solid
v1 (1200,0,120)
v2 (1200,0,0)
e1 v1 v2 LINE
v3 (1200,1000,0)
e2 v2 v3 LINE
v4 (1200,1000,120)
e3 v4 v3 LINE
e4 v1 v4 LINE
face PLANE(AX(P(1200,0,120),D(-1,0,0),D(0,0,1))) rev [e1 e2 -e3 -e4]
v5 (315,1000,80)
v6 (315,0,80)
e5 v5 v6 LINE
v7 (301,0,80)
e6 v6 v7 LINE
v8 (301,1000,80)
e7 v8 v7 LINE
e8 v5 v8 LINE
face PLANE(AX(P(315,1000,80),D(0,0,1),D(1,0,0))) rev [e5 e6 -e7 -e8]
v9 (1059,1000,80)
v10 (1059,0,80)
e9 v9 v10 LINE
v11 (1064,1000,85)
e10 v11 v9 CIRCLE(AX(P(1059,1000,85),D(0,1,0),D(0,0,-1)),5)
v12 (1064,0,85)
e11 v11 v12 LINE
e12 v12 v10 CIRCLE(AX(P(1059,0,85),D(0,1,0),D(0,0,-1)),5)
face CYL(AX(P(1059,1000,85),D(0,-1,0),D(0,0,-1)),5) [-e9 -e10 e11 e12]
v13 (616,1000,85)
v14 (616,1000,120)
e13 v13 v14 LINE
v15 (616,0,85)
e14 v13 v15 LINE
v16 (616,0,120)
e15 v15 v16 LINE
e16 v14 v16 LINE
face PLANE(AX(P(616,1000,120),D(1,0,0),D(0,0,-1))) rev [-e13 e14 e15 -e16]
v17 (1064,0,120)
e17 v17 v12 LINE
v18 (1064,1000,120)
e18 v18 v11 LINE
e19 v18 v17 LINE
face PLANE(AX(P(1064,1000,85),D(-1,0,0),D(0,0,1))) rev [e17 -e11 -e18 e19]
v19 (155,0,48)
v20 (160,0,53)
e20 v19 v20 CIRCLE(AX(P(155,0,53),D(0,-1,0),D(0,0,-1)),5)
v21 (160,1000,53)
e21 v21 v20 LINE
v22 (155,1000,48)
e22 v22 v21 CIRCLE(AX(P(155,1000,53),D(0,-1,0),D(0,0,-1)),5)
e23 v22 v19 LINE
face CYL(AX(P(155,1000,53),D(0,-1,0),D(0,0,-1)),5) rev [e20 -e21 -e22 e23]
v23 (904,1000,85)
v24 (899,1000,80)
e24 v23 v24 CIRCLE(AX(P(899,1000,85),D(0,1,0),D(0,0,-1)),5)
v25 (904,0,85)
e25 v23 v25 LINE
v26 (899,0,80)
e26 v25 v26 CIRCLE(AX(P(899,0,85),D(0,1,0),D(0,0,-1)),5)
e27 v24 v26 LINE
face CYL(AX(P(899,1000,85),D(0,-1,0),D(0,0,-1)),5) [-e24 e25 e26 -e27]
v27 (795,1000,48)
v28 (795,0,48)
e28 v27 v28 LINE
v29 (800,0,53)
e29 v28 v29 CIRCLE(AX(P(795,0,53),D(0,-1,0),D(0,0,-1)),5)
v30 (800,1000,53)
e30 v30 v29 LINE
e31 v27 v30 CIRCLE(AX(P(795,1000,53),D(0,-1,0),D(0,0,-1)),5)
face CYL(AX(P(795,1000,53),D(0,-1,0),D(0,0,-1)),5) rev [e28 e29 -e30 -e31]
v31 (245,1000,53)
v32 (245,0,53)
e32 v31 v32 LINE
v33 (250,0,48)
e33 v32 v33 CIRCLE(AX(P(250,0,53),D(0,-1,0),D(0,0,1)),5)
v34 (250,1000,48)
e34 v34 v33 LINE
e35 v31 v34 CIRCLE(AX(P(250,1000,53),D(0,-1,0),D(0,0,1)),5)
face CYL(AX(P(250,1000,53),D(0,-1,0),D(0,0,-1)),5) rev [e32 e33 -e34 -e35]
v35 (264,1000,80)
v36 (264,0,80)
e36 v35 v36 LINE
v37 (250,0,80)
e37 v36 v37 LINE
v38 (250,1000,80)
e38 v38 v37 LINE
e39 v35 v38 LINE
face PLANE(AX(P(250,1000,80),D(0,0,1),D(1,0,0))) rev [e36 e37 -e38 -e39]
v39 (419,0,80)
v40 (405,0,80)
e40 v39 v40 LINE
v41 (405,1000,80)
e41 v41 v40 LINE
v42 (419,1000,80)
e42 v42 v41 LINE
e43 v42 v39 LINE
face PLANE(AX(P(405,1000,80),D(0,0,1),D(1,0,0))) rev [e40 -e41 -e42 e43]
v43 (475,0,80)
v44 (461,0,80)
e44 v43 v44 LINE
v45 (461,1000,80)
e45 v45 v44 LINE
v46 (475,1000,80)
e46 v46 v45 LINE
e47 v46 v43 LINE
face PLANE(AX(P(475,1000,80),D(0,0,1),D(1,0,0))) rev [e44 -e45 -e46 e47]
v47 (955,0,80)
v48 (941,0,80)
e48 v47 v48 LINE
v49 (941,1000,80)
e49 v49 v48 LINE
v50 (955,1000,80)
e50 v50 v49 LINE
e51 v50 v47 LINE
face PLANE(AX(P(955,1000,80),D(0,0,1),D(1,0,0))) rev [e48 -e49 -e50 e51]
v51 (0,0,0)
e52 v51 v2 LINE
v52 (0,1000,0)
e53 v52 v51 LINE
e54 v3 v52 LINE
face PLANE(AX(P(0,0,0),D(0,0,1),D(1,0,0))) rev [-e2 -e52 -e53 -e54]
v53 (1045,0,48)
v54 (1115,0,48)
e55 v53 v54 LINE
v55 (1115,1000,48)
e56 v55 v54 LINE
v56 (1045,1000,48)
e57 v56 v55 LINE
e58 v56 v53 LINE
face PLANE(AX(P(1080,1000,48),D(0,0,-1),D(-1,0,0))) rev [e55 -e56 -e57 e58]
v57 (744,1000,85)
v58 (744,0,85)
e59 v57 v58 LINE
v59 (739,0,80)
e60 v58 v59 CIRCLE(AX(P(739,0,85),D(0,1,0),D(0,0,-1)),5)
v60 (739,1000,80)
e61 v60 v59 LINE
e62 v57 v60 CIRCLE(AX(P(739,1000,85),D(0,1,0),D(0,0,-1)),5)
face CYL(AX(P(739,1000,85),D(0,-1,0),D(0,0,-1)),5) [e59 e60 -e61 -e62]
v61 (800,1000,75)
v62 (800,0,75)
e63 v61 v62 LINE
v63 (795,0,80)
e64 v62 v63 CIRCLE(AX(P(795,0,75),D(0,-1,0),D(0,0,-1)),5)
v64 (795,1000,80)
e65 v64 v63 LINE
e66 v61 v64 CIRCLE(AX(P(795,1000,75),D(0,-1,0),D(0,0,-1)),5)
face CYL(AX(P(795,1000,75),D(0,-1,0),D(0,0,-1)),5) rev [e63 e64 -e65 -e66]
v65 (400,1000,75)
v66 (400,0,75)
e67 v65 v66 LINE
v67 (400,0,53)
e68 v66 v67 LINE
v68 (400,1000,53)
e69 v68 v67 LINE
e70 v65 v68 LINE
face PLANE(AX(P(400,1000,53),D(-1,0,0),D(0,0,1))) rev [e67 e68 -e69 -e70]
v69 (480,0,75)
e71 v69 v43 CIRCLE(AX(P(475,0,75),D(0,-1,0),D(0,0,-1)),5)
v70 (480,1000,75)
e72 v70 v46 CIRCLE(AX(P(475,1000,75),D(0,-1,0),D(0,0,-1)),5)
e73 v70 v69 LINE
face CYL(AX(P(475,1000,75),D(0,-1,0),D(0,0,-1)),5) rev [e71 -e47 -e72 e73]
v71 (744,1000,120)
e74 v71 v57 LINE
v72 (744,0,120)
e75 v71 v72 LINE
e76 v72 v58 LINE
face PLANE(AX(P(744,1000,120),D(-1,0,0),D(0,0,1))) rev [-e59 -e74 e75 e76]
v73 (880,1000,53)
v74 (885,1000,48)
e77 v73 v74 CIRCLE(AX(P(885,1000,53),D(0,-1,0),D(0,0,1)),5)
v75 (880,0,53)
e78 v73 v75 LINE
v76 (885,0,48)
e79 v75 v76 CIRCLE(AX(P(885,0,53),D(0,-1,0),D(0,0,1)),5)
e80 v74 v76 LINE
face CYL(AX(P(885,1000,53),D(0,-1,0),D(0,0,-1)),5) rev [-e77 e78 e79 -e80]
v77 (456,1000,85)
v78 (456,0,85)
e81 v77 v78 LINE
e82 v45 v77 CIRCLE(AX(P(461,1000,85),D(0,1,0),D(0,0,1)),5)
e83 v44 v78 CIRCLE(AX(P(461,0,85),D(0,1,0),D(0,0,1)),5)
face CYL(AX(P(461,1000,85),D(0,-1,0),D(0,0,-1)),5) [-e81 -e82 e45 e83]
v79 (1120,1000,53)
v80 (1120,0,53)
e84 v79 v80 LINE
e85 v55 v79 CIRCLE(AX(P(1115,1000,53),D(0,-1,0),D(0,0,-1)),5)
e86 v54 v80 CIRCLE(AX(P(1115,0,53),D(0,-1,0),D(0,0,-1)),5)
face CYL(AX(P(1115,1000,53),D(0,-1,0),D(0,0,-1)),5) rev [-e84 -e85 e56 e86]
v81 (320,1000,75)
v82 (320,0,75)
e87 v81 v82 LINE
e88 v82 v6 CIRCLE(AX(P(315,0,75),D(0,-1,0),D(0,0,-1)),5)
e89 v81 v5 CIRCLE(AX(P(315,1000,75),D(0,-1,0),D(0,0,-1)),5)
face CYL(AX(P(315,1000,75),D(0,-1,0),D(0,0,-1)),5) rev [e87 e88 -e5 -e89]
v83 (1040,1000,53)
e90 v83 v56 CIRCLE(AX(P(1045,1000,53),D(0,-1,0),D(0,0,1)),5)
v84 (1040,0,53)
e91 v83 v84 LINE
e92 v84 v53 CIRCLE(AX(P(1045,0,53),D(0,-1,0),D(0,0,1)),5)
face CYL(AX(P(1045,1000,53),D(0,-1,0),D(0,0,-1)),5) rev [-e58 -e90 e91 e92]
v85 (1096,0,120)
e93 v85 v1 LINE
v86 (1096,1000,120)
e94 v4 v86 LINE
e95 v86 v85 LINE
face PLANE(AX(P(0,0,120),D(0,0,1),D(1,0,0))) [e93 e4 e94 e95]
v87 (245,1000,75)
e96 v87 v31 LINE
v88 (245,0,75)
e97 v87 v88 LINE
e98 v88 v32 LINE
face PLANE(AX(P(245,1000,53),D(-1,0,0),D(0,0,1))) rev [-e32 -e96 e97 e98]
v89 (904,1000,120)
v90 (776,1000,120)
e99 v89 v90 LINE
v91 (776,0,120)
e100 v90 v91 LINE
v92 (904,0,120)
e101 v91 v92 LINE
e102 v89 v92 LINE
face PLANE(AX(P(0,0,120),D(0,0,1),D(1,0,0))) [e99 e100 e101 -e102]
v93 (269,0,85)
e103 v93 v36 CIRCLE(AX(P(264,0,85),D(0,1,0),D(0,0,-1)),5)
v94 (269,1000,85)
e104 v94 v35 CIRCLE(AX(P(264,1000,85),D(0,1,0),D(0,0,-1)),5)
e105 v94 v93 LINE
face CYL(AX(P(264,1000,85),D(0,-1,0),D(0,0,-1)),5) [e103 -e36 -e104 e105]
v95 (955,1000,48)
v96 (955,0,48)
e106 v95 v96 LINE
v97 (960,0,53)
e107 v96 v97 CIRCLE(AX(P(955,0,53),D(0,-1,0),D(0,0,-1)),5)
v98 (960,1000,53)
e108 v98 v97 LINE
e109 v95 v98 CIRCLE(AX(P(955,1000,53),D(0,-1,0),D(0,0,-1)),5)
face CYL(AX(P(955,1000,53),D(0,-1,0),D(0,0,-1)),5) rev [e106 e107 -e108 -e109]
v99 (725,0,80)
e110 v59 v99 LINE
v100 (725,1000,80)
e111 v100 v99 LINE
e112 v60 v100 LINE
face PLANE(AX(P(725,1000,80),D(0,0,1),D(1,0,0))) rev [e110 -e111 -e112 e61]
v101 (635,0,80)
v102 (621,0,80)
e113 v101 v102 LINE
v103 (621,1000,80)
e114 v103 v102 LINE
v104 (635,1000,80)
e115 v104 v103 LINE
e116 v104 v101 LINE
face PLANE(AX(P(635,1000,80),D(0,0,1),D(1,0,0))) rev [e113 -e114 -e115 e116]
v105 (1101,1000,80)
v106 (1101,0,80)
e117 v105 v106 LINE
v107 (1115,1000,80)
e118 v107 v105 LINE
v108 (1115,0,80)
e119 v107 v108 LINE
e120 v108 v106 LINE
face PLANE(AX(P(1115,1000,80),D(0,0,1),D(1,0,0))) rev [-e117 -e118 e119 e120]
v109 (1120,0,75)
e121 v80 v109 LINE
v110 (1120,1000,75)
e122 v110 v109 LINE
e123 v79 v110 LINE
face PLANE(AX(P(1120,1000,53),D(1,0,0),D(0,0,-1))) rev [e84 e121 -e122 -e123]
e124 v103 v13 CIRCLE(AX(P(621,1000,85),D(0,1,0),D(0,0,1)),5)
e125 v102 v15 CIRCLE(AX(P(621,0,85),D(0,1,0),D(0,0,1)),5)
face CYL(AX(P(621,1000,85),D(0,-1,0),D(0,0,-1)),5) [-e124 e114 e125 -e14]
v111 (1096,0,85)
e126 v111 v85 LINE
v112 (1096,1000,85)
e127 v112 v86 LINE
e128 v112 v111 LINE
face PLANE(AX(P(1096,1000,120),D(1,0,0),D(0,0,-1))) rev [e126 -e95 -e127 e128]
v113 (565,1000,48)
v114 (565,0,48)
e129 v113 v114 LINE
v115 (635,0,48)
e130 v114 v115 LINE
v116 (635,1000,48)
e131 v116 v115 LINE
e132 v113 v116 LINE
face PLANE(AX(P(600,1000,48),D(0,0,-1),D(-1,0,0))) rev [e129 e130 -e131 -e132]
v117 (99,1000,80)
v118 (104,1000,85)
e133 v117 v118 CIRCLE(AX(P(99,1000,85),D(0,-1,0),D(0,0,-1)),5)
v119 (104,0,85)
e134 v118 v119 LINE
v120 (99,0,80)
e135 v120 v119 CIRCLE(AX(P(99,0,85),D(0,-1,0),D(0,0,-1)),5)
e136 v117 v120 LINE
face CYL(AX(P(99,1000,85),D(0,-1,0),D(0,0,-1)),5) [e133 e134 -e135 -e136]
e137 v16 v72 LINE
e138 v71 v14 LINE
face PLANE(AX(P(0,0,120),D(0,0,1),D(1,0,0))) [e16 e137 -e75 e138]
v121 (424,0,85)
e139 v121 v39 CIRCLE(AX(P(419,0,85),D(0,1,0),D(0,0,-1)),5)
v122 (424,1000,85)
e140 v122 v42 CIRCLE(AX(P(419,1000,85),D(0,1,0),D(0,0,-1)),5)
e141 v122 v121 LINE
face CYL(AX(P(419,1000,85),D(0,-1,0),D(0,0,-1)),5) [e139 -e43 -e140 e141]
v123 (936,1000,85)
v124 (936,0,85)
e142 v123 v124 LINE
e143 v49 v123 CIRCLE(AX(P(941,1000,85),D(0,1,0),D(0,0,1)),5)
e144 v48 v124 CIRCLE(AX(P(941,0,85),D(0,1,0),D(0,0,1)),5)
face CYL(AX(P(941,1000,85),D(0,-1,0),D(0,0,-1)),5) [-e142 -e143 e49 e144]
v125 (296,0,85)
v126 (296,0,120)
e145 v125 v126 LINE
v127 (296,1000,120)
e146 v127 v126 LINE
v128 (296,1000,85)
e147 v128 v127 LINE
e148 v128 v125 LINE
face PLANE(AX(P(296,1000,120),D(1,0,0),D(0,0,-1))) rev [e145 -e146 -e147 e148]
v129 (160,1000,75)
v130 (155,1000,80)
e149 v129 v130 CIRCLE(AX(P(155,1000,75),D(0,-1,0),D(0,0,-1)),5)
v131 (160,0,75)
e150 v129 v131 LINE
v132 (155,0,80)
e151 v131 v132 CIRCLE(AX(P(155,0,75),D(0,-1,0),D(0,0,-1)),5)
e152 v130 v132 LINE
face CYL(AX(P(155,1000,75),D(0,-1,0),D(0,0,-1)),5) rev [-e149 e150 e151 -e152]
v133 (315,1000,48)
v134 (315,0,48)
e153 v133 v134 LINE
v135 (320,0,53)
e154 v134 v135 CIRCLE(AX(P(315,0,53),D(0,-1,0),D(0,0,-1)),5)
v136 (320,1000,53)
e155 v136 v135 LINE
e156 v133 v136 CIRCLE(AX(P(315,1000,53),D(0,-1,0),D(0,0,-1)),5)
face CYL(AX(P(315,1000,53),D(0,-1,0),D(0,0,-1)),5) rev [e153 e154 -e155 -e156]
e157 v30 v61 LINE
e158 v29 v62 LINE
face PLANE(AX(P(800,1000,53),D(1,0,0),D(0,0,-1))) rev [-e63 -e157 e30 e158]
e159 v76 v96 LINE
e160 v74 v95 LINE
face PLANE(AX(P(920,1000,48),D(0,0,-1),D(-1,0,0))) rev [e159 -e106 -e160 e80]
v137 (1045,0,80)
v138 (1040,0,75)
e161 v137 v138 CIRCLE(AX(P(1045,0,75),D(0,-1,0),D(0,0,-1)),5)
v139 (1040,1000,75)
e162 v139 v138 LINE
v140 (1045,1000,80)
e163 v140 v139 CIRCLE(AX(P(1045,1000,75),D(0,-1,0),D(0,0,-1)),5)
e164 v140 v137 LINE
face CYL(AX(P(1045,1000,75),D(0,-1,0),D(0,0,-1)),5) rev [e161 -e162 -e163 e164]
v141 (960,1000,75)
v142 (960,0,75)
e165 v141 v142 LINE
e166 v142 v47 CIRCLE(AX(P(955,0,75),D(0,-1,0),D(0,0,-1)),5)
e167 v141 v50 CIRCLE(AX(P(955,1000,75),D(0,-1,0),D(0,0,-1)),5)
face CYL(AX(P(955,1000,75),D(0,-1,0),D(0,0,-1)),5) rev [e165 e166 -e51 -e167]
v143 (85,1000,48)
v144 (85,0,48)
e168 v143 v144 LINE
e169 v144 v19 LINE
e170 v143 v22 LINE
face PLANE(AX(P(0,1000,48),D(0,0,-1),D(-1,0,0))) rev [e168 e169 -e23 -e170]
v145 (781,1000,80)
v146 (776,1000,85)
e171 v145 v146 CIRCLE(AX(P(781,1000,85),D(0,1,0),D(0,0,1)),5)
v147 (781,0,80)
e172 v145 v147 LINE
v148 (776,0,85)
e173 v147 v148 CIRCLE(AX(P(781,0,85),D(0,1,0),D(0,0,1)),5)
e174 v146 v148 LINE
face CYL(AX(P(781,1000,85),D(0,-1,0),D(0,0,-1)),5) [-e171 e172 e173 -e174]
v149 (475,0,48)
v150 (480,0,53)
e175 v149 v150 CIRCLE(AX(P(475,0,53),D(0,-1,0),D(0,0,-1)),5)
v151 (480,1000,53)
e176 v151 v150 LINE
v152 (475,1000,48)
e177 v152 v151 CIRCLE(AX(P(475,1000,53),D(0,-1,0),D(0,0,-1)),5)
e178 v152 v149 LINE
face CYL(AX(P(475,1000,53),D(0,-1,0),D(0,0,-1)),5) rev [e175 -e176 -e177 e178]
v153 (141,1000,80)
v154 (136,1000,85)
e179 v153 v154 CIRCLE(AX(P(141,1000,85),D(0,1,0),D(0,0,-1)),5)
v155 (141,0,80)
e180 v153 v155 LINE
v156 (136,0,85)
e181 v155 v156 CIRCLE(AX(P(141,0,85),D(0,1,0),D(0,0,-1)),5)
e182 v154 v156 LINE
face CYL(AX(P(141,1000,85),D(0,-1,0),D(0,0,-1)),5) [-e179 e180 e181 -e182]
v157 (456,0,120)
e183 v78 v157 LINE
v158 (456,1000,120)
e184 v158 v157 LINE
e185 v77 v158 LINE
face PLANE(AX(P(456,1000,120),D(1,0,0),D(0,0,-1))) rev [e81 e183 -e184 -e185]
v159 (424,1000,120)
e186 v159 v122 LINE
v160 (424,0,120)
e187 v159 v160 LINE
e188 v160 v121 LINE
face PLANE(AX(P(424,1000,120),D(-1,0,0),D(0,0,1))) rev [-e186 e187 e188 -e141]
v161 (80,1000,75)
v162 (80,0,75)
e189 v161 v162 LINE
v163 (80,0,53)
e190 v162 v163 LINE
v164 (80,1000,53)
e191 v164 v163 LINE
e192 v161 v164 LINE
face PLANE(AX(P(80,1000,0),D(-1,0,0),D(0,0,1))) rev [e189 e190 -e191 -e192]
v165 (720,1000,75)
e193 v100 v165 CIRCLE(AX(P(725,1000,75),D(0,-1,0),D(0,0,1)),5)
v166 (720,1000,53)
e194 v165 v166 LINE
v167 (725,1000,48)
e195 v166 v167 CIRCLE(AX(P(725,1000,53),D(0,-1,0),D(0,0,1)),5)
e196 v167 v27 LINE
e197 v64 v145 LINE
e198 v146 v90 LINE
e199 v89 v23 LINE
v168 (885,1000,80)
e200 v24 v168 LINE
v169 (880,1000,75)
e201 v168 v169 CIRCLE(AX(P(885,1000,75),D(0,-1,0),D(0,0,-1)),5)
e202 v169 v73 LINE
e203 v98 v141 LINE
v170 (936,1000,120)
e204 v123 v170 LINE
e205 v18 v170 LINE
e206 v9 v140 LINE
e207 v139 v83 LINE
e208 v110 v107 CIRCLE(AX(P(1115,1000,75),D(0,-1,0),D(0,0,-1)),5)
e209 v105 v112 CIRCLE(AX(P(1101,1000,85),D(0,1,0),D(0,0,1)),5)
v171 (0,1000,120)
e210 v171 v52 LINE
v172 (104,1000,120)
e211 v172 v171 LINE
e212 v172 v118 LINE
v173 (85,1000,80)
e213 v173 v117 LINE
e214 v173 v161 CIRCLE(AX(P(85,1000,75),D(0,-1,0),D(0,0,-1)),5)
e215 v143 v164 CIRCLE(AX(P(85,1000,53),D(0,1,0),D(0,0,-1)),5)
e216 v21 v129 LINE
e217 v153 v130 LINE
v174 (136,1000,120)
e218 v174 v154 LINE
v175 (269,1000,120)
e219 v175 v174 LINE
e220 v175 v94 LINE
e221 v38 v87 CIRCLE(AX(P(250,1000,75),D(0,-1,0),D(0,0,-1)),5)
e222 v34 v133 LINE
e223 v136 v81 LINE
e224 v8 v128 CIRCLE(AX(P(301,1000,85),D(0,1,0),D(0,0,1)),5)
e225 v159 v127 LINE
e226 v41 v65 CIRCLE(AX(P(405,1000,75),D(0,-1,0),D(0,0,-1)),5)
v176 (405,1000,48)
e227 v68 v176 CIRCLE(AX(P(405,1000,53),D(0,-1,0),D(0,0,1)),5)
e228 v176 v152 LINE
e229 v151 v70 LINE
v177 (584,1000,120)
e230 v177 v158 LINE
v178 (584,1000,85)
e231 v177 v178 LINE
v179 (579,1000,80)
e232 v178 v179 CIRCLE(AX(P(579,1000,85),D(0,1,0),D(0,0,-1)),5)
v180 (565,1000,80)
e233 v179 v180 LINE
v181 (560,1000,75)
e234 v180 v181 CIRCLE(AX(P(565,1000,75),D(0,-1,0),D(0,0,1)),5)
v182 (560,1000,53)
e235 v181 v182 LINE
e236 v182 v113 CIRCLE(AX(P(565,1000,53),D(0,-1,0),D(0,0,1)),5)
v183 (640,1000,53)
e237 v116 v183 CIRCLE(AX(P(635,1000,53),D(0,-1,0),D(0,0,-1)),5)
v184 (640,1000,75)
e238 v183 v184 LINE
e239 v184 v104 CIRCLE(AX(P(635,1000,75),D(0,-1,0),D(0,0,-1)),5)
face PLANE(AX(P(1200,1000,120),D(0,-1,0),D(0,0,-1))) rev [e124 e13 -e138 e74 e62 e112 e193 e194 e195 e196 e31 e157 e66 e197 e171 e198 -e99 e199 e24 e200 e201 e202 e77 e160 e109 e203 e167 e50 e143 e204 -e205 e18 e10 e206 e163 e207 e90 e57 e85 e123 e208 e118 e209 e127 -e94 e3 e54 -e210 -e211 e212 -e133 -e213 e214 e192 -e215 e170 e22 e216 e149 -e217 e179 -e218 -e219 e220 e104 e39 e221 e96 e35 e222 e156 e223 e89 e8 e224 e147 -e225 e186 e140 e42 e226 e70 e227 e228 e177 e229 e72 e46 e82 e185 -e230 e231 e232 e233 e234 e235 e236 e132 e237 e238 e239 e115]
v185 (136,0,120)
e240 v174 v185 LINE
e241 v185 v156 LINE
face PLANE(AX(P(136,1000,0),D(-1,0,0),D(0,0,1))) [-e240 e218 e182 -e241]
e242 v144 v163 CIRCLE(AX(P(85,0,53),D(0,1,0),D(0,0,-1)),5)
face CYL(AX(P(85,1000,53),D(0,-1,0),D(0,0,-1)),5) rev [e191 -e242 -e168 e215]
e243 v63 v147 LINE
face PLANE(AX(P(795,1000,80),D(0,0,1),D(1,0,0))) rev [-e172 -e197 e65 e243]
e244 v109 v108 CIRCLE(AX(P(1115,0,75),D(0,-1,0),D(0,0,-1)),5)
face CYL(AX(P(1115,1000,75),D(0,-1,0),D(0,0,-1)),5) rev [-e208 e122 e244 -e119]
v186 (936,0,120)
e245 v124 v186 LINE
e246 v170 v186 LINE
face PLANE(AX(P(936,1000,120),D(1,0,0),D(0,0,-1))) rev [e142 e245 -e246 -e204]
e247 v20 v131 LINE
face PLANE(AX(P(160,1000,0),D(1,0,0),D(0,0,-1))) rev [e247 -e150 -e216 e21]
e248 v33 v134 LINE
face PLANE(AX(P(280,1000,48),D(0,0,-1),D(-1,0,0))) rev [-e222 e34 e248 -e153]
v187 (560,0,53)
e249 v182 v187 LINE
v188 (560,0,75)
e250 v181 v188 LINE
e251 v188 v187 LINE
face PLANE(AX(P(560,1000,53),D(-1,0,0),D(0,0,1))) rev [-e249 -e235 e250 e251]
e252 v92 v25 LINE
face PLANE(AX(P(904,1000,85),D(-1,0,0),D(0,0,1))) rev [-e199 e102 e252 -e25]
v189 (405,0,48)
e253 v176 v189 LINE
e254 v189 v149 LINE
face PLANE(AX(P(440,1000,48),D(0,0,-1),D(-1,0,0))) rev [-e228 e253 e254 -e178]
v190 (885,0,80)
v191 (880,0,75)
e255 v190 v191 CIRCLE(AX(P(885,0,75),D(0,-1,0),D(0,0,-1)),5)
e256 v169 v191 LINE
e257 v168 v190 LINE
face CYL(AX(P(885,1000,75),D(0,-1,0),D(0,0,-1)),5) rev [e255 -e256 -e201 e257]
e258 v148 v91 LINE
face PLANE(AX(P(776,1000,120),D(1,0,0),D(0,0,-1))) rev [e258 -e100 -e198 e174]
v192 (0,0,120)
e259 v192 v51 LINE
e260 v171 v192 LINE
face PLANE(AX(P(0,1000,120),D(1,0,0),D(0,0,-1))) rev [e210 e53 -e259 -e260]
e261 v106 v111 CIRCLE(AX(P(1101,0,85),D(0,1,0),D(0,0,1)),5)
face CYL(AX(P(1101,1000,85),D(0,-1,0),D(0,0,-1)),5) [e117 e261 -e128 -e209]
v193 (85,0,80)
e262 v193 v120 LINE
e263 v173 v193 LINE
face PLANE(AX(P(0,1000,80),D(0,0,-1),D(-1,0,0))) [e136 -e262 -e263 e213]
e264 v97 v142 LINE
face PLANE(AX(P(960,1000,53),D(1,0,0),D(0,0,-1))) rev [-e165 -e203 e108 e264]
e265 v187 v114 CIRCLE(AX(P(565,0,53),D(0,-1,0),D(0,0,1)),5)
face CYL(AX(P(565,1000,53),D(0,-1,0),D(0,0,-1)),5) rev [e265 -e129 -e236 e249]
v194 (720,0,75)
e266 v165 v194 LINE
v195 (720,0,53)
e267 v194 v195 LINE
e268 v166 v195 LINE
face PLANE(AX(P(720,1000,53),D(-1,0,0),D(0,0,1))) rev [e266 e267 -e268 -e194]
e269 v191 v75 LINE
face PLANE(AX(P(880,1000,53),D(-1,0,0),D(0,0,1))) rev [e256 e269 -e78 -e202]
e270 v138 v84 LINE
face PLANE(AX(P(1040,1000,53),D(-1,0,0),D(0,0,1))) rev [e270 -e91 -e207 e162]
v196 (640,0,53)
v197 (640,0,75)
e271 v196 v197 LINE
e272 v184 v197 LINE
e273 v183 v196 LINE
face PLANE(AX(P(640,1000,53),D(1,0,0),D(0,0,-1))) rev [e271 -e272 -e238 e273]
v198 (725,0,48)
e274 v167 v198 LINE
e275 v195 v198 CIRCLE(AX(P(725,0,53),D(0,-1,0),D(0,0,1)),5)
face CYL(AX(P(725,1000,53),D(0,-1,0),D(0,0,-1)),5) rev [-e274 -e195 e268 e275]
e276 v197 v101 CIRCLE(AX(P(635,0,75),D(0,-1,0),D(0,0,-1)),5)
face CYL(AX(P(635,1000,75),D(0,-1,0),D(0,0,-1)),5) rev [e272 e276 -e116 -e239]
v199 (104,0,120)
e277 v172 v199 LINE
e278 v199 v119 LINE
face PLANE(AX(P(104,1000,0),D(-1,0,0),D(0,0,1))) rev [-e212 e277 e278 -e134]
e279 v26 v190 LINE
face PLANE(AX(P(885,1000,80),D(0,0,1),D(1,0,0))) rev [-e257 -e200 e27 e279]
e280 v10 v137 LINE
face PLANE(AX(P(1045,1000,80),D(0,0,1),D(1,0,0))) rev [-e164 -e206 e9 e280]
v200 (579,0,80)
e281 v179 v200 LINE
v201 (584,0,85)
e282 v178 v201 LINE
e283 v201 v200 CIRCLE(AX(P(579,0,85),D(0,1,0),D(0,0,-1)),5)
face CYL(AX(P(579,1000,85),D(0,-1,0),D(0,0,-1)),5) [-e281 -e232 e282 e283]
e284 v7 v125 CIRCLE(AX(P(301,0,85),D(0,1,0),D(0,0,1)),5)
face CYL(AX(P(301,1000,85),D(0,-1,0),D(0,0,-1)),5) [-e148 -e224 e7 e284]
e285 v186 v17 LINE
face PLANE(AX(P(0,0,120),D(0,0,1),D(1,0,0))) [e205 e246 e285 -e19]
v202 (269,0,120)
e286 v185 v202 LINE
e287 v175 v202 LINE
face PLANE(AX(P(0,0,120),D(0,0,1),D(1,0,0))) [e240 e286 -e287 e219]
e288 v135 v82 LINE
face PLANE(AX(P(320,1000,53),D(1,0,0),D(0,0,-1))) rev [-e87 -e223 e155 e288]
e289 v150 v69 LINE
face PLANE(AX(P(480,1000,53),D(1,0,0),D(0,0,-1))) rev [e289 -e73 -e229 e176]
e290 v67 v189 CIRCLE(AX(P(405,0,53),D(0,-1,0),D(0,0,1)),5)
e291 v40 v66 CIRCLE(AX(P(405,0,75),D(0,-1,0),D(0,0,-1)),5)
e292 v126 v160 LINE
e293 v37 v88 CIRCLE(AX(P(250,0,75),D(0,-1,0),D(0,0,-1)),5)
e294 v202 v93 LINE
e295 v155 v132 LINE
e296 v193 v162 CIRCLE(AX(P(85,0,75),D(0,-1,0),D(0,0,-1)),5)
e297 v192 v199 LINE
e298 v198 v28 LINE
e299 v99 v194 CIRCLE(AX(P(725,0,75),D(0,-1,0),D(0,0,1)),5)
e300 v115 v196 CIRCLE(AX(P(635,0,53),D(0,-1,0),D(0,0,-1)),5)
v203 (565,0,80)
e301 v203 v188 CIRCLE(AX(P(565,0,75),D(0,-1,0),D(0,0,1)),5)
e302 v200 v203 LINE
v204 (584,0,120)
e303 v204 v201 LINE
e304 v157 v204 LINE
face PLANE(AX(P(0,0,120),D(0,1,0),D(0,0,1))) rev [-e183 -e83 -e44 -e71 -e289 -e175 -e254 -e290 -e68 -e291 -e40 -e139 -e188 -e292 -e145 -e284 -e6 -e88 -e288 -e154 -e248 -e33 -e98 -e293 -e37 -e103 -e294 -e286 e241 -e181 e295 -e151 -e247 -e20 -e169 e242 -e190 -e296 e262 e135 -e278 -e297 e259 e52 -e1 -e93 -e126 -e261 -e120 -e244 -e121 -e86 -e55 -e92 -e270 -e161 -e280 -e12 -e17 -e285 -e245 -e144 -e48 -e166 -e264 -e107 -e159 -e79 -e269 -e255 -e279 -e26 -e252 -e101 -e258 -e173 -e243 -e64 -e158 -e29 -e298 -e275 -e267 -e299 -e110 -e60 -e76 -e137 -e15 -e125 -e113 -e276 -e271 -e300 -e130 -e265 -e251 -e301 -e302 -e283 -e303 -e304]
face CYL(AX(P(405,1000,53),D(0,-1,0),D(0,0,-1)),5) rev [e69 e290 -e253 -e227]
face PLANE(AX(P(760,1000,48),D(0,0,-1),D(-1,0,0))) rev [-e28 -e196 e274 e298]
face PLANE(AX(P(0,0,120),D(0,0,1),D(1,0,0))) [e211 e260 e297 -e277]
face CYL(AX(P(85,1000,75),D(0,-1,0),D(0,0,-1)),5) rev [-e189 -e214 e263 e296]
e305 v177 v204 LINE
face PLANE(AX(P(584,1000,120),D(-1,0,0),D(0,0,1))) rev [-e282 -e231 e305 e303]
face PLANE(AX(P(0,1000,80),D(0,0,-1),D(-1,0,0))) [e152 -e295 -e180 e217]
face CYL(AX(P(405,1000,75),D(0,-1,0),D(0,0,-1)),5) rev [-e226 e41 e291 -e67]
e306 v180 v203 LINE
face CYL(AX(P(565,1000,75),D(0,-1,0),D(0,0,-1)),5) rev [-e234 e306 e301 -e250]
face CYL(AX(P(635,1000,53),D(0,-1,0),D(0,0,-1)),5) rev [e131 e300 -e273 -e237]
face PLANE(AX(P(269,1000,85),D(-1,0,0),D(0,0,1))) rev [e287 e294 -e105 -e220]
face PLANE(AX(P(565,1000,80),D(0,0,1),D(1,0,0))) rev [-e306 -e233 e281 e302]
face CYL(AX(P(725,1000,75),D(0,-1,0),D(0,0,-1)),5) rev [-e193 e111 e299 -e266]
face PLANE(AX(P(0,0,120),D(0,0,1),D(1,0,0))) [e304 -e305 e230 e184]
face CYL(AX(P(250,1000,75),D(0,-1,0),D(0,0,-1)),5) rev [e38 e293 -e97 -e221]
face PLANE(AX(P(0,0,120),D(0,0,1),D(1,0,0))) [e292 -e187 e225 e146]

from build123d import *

# Parameters (mm, degrees)
PLATE_OUTLINE_SKETCH_W = 1200
PLATE_OUTLINE_SKETCH_H = 1000
BASE_PLATE_120MM_DEPTH = 120
T_SLOTS_SET_A_DEPTH    = 1000
T_SLOTS_SET_B_DEPTH    = 1000


with BuildPart() as part:
    # Plate Outline Sketch → Base Plate 120mm (new body)
    with BuildSketch(Plane.XY):
        with Locations((600, 500)):
            Rectangle(PLATE_OUTLINE_SKETCH_W, PLATE_OUTLINE_SKETCH_H)
    extrude(amount=BASE_PLATE_120MM_DEPTH)

    # T-Slot Profiles Set A Sketch → T-Slots Set A (cut)
    with BuildSketch(Plane.XZ):
        with BuildLine():
            Line((99, 80), (85, 80))
            ThreePointArc((85, 80), (81.464466094, 78.535533906), (80, 75))
            Line((80, 75), (80, 53))
            ThreePointArc((80, 53), (81.464466094, 49.464466094), (85, 48))
            Line((85, 48), (155, 48))
            ThreePointArc((155, 48), (158.535533906, 49.464466094), (160, 53))
            Line((160, 53), (160, 75))
            ThreePointArc((160, 75), (158.535533906, 78.535533906), (155, 80))
            Line((155, 80), (141, 80))
            ThreePointArc((141, 80), (137.464466094, 81.464466094), (136, 85))
            Line((136, 85), (136, 120))
            Line((136, 120), (104, 120))
            Line((104, 120), (104, 85))
            ThreePointArc((104, 85), (102.535533906, 81.464466094), (99, 80))
        make_face()
    extrude(amount=-T_SLOTS_SET_A_DEPTH, mode=Mode.SUBTRACT)

    # T-Slot Profiles Set B Sketch → T-Slots Set B (cut)
    with BuildSketch(Plane.XZ):
        with BuildLine():
            Line((269, 120), (296, 120))
            Line((296, 120), (296, 85))
            ThreePointArc((296, 85), (297.464466094, 81.464466094), (301, 80))
            Line((301, 80), (315, 80))
            ThreePointArc((315, 80), (318.535533906, 78.535533906), (320, 75))
            Line((320, 75), (320, 53))
            ThreePointArc((320, 53), (318.535533906, 49.464466094), (315, 48))
            Line((315, 48), (280, 48))
            Line((280, 48), (250, 48))
            ThreePointArc((250, 48), (246.464466094, 49.464466094), (245, 53))
            Line((245, 53), (245, 75))
            ThreePointArc((245, 75), (246.464466094, 78.535533906), (250, 80))
            Line((250, 80), (264, 80))
            ThreePointArc((264, 80), (267.535533906, 81.464466094), (269, 85))
            Line((269, 85), (269, 120))
        make_face()
        with BuildLine():
            Line((424, 120), (456, 120))
            Line((456, 120), (456, 85))
            ThreePointArc((456, 85), (457.464466094, 81.464466094), (461, 80))
            Line((461, 80), (475, 80))
            ThreePointArc((475, 80), (478.535533906, 78.535533906), (480, 75))
            Line((480, 75), (480, 53))
            ThreePointArc((480, 53), (478.535533906, 49.464466094), (475, 48))
            Line((475, 48), (440, 48))
            Line((440, 48), (405, 48))
            ThreePointArc((405, 48), (401.464466094, 49.464466094), (400, 53))
            Line((400, 53), (400, 75))
            ThreePointArc((400, 75), (401.464466094, 78.535533906), (405, 80))
            Line((405, 80), (419, 80))
            ThreePointArc((419, 80), (422.535533906, 81.464466094), (424, 85))
            Line((424, 85), (424, 120))
        make_face()
        with BuildLine():
            Line((584, 120), (616, 120))
            Line((616, 120), (616, 85))
            ThreePointArc((616, 85), (617.464466094, 81.464466094), (621, 80))
            Line((621, 80), (635, 80))
            ThreePointArc((635, 80), (638.535533906, 78.535533906), (640, 75))
            Line((640, 75), (640, 53))
            ThreePointArc((640, 53), (638.535533906, 49.464466094), (635, 48))
            Line((635, 48), (600, 48))
            Line((600, 48), (565, 48))
            ThreePointArc((565, 48), (561.464466094, 49.464466094), (560, 53))
            Line((560, 53), (560, 75))
            ThreePointArc((560, 75), (561.464466094, 78.535533906), (565, 80))
            Line((565, 80), (579, 80))
            ThreePointArc((579, 80), (582.535533906, 81.464466094), (584, 85))
            Line((584, 85), (584, 120))
        make_face()
        with BuildLine():
            Line((744, 120), (776, 120))
            Line((776, 120), (776, 85))
            ThreePointArc((776, 85), (777.464466094, 81.464466094), (781, 80))
            Line((781, 80), (795, 80))
            ThreePointArc((795, 80), (798.535533906, 78.535533906), (800, 75))
            Line((800, 75), (800, 53))
            ThreePointArc((800, 53), (798.535533906, 49.464466094), (795, 48))
            Line((795, 48), (760, 48))
            Line((760, 48), (725, 48))
            ThreePointArc((725, 48), (721.464466094, 49.464466094), (720, 53))
            Line((720, 53), (720, 75))
            ThreePointArc((720, 75), (721.464466094, 78.535533906), (725, 80))
            Line((725, 80), (739, 80))
            ThreePointArc((739, 80), (742.535533906, 81.464466094), (744, 85))
            Line((744, 85), (744, 120))
        make_face()
        with BuildLine():
            Line((904, 120), (936, 120))
            Line((936, 120), (936, 85))
            ThreePointArc((936, 85), (937.464466094, 81.464466094), (941, 80))
            Line((941, 80), (955, 80))
            ThreePointArc((955, 80), (958.535533906, 78.535533906), (960, 75))
            Line((960, 75), (960, 53))
            ThreePointArc((960, 53), (958.535533906, 49.464466094), (955, 48))
            Line((955, 48), (920, 48))
            Line((920, 48), (885, 48))
            ThreePointArc((885, 48), (881.464466094, 49.464466094), (880, 53))
            Line((880, 53), (880, 75))
            ThreePointArc((880, 75), (881.464466094, 78.535533906), (885, 80))
            Line((885, 80), (899, 80))
            ThreePointArc((899, 80), (902.535533906, 81.464466094), (904, 85))
            Line((904, 85), (904, 120))
        make_face()
        with BuildLine():
            Line((1064, 120), (1096, 120))
            Line((1096, 120), (1096, 85))
            ThreePointArc((1096, 85), (1097.464466094, 81.464466094), (1101, 80))
            Line((1101, 80), (1115, 80))
            ThreePointArc((1115, 80), (1118.535533906, 78.535533906), (1120, 75))
            Line((1120, 75), (1120, 53))
            ThreePointArc((1120, 53), (1118.535533906, 49.464466094), (1115, 48))
            Line((1115, 48), (1080, 48))
            Line((1080, 48), (1045, 48))
            ThreePointArc((1045, 48), (1041.464466094, 49.464466094), (1040, 53))
            Line((1040, 53), (1040, 75))
            ThreePointArc((1040, 75), (1041.464466094, 78.535533906), (1045, 80))
            Line((1045, 80), (1059, 80))
            ThreePointArc((1059, 80), (1062.535533906, 81.464466094), (1064, 85))
            Line((1064, 85), (1064, 120))
        make_face()
    extrude(amount=-T_SLOTS_SET_B_DEPTH, mode=Mode.SUBTRACT)


solid = part.part
